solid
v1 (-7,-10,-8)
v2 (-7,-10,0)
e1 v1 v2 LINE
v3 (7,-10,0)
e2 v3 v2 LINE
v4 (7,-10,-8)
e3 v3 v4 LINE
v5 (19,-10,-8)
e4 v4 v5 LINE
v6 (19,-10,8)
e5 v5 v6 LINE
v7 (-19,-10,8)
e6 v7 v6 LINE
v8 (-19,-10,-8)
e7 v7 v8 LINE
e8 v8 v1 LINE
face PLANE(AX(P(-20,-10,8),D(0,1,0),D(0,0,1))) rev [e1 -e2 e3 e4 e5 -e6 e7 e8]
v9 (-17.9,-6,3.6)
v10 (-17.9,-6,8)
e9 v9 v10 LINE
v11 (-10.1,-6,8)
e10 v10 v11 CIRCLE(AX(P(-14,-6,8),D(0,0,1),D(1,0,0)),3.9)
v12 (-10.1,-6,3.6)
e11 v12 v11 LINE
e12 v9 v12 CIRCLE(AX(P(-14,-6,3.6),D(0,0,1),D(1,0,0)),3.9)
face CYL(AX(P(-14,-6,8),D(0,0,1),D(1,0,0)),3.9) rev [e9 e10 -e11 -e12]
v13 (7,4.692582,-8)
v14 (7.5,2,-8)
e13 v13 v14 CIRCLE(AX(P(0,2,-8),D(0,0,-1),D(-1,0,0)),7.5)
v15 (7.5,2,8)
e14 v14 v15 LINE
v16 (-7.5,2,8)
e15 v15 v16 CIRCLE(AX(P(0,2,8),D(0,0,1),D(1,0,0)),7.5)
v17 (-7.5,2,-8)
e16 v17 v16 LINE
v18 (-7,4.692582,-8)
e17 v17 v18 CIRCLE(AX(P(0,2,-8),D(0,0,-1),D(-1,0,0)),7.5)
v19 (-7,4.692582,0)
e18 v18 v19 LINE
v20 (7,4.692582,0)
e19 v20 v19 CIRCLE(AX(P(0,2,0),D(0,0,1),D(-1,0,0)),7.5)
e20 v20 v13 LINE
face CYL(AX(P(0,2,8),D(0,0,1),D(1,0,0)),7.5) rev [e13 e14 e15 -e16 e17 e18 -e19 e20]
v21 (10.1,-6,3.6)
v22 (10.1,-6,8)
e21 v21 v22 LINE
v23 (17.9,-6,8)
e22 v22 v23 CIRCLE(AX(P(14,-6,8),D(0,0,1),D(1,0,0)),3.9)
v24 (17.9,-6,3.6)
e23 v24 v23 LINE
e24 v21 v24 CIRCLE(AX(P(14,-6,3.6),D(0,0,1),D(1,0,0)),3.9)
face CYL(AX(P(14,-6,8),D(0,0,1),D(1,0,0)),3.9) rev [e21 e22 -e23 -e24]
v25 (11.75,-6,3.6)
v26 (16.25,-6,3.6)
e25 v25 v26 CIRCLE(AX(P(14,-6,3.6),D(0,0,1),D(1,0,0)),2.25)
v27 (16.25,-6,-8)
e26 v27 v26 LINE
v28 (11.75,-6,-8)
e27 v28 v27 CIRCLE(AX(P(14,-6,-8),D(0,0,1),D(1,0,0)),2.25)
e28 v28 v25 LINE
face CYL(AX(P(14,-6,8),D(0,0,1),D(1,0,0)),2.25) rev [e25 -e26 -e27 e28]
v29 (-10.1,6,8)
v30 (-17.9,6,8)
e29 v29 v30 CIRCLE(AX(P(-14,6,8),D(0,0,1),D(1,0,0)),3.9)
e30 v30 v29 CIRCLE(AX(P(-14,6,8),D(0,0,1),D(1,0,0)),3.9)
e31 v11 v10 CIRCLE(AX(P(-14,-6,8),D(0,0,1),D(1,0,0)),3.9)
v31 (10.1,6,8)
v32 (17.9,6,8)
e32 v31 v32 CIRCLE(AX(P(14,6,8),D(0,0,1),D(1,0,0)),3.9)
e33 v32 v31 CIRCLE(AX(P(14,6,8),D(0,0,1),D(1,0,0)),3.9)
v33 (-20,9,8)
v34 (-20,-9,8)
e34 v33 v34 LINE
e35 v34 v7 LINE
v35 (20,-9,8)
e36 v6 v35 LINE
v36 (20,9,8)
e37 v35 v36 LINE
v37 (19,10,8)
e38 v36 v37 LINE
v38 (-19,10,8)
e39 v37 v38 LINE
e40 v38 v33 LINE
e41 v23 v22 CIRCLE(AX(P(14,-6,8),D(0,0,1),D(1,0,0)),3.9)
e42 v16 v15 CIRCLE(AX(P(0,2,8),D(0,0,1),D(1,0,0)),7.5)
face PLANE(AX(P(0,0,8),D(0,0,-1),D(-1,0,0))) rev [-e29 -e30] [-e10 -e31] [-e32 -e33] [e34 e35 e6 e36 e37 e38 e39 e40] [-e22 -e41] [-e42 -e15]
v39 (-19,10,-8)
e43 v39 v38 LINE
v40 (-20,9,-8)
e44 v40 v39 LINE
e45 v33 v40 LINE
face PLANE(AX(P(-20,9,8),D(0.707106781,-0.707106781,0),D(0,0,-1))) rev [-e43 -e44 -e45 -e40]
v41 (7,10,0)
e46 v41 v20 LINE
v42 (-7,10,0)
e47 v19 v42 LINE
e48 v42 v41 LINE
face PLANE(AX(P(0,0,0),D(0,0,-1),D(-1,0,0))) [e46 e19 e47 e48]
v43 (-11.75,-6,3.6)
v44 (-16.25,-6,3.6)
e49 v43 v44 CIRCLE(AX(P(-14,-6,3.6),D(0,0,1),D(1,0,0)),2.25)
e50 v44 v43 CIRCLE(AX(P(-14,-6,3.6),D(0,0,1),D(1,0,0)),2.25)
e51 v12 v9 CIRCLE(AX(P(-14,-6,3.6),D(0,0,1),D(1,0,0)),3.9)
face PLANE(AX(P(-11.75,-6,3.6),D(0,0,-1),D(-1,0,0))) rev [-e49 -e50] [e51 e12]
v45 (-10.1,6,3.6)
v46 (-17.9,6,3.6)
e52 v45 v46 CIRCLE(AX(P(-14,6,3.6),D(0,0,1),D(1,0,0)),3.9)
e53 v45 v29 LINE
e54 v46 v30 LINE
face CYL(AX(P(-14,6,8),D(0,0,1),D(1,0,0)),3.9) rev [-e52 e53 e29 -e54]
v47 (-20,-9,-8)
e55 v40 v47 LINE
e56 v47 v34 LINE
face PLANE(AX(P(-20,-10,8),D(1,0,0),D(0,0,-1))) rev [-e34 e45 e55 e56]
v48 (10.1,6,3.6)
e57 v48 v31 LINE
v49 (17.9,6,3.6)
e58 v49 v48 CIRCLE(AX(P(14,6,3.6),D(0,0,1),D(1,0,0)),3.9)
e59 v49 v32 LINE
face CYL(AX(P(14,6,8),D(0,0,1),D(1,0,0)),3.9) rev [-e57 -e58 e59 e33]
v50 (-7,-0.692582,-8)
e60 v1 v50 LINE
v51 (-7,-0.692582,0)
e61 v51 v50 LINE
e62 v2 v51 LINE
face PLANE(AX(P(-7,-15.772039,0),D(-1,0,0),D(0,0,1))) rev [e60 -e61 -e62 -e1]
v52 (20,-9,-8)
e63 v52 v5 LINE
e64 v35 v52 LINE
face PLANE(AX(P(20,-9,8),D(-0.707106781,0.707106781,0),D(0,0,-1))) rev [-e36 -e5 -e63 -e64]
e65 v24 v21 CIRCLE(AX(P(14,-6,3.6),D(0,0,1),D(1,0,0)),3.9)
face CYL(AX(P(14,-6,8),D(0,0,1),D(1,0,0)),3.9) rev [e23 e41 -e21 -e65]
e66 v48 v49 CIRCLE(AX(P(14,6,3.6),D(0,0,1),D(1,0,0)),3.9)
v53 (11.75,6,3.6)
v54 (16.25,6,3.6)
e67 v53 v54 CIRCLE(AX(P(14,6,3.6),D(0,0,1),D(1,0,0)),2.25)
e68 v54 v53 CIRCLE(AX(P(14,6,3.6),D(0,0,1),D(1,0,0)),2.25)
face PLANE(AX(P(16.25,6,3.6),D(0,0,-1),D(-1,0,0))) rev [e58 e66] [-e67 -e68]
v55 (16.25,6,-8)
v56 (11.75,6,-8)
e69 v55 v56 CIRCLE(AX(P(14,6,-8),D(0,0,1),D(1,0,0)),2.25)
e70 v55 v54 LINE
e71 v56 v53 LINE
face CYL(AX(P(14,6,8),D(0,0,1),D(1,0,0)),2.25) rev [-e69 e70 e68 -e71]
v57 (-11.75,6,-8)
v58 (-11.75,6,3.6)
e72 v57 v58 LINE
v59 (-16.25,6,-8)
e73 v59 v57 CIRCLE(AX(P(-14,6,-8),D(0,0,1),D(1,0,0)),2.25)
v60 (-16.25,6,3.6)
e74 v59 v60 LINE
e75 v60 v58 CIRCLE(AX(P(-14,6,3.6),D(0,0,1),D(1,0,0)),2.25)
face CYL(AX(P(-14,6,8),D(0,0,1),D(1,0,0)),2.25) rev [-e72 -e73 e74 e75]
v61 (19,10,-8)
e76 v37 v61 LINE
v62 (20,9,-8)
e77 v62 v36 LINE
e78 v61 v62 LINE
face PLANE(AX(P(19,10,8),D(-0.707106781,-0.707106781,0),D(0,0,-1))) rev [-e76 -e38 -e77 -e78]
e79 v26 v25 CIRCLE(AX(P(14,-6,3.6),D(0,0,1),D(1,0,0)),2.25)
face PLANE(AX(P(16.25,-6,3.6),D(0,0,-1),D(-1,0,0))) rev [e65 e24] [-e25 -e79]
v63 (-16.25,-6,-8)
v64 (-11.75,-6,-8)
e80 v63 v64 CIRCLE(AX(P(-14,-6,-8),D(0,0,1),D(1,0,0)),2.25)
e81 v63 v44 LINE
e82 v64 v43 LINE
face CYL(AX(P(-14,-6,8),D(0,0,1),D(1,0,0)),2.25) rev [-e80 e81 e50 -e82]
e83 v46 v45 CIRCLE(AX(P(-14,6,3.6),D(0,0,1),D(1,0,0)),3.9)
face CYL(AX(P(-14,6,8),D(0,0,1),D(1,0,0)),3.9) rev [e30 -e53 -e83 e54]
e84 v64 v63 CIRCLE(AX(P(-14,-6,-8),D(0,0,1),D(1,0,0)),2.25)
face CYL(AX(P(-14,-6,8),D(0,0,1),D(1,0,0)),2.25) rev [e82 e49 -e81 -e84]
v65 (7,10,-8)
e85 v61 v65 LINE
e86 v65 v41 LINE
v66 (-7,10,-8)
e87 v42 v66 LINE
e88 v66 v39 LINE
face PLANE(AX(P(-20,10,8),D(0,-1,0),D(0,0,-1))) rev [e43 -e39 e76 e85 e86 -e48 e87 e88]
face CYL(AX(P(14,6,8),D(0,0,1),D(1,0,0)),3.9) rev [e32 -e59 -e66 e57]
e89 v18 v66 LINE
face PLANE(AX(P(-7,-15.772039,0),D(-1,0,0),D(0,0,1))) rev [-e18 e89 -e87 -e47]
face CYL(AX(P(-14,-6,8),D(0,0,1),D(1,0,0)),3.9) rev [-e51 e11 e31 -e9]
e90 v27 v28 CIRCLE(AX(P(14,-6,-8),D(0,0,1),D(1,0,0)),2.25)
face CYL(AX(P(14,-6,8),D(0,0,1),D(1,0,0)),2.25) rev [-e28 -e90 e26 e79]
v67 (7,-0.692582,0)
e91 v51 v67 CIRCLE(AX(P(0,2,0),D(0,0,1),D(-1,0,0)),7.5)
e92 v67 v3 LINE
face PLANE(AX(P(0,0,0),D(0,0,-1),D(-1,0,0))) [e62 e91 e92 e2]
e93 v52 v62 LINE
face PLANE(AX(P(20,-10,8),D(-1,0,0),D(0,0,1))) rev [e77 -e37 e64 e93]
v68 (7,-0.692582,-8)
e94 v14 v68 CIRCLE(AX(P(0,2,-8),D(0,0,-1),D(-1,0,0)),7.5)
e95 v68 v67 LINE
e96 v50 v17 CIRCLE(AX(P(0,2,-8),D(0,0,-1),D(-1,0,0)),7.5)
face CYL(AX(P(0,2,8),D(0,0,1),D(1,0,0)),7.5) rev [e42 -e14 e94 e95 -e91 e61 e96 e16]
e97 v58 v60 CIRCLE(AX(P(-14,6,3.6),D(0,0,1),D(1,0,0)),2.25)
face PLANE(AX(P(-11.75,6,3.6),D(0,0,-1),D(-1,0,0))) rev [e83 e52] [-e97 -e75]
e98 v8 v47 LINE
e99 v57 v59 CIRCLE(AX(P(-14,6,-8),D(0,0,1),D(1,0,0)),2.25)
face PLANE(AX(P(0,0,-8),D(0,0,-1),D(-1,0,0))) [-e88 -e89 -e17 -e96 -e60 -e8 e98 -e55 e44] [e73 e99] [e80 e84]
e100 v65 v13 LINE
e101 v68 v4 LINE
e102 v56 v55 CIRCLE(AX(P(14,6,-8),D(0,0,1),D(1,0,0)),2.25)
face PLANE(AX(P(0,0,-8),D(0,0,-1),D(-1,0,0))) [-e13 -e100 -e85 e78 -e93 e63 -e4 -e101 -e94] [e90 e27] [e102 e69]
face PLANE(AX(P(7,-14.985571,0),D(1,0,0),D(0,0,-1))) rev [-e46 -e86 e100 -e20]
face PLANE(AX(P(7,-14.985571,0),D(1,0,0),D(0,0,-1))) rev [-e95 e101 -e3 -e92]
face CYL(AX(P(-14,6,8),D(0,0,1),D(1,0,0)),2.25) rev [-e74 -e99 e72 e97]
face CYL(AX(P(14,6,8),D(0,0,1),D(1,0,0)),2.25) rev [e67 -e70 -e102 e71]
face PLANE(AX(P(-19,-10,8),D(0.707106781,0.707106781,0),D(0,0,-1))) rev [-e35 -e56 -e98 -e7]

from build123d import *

# Parameters (mm, degrees)
SKETCH_1_W                   = 40
SKETCH_1_H                   = 20
EXTRUDE_1_DEPTH              = 8
CHAMFER_1_SIZE               = 1
HOLE_WIZARD_15_0_15_1_D      = 15
HOLE_WIZARD_15_0_15_1_DEPTH  = 20
CUT_EXTRUDE_2_DEPTH          = 8
HOLE_WIZARD_M4_3_D           = 4.5
HOLE_WIZARD_M4_3_CBORE_D     = 7.8
HOLE_WIZARD_M4_3_CBORE_DEPTH = 4.4


with BuildPart() as part:
    # 草图1 → 凸台-拉伸1 (new, symmetric)
    with BuildSketch(Plane.XY):
        Rectangle(SKETCH_1_W, SKETCH_1_H)
    extrude(amount=EXTRUDE_1_DEPTH, both=True)

    # 倒角1
    chamfer_1_edges = [part.edges().sort_by_distance(p)[0] for p in [
        (20, -10, 0),
        (-20, -10, 0),
        (-20, 10, 0),
        (20, 10, 0),
    ]]
    chamfer(chamfer_1_edges, length=CHAMFER_1_SIZE)

    # Ø15.0 (15) 直径孔1
    with Locations(Plane.XY.offset(8)):
        with Locations((0, 2)):
            Hole(HOLE_WIZARD_15_0_15_1_D / 2, depth=HOLE_WIZARD_15_0_15_1_DEPTH)

    # 草图6 → 切除-拉伸2 (cut)
    with BuildSketch(Plane(origin=(0, 0, -8), x_dir=(-1, 0, 0), z_dir=(0, 0, -1))):
        Polygon((-7, -14.985571338), (-7, 13.139303821), (7, 13.139303821), (7, -15.772038878), align=None)
    extrude(amount=-CUT_EXTRUDE_2_DEPTH, mode=Mode.SUBTRACT)

    # M4 六角凹头螺钉的柱形沉头孔3 (through all)
    with Locations(Plane.XY.offset(8)):
        with Locations((0, 0), (14, 6), (-14, -6), (-14, 6), (14, -6)):
            CounterBoreHole(HOLE_WIZARD_M4_3_D / 2, HOLE_WIZARD_M4_3_CBORE_D / 2, HOLE_WIZARD_M4_3_CBORE_DEPTH)


solid = part.part
